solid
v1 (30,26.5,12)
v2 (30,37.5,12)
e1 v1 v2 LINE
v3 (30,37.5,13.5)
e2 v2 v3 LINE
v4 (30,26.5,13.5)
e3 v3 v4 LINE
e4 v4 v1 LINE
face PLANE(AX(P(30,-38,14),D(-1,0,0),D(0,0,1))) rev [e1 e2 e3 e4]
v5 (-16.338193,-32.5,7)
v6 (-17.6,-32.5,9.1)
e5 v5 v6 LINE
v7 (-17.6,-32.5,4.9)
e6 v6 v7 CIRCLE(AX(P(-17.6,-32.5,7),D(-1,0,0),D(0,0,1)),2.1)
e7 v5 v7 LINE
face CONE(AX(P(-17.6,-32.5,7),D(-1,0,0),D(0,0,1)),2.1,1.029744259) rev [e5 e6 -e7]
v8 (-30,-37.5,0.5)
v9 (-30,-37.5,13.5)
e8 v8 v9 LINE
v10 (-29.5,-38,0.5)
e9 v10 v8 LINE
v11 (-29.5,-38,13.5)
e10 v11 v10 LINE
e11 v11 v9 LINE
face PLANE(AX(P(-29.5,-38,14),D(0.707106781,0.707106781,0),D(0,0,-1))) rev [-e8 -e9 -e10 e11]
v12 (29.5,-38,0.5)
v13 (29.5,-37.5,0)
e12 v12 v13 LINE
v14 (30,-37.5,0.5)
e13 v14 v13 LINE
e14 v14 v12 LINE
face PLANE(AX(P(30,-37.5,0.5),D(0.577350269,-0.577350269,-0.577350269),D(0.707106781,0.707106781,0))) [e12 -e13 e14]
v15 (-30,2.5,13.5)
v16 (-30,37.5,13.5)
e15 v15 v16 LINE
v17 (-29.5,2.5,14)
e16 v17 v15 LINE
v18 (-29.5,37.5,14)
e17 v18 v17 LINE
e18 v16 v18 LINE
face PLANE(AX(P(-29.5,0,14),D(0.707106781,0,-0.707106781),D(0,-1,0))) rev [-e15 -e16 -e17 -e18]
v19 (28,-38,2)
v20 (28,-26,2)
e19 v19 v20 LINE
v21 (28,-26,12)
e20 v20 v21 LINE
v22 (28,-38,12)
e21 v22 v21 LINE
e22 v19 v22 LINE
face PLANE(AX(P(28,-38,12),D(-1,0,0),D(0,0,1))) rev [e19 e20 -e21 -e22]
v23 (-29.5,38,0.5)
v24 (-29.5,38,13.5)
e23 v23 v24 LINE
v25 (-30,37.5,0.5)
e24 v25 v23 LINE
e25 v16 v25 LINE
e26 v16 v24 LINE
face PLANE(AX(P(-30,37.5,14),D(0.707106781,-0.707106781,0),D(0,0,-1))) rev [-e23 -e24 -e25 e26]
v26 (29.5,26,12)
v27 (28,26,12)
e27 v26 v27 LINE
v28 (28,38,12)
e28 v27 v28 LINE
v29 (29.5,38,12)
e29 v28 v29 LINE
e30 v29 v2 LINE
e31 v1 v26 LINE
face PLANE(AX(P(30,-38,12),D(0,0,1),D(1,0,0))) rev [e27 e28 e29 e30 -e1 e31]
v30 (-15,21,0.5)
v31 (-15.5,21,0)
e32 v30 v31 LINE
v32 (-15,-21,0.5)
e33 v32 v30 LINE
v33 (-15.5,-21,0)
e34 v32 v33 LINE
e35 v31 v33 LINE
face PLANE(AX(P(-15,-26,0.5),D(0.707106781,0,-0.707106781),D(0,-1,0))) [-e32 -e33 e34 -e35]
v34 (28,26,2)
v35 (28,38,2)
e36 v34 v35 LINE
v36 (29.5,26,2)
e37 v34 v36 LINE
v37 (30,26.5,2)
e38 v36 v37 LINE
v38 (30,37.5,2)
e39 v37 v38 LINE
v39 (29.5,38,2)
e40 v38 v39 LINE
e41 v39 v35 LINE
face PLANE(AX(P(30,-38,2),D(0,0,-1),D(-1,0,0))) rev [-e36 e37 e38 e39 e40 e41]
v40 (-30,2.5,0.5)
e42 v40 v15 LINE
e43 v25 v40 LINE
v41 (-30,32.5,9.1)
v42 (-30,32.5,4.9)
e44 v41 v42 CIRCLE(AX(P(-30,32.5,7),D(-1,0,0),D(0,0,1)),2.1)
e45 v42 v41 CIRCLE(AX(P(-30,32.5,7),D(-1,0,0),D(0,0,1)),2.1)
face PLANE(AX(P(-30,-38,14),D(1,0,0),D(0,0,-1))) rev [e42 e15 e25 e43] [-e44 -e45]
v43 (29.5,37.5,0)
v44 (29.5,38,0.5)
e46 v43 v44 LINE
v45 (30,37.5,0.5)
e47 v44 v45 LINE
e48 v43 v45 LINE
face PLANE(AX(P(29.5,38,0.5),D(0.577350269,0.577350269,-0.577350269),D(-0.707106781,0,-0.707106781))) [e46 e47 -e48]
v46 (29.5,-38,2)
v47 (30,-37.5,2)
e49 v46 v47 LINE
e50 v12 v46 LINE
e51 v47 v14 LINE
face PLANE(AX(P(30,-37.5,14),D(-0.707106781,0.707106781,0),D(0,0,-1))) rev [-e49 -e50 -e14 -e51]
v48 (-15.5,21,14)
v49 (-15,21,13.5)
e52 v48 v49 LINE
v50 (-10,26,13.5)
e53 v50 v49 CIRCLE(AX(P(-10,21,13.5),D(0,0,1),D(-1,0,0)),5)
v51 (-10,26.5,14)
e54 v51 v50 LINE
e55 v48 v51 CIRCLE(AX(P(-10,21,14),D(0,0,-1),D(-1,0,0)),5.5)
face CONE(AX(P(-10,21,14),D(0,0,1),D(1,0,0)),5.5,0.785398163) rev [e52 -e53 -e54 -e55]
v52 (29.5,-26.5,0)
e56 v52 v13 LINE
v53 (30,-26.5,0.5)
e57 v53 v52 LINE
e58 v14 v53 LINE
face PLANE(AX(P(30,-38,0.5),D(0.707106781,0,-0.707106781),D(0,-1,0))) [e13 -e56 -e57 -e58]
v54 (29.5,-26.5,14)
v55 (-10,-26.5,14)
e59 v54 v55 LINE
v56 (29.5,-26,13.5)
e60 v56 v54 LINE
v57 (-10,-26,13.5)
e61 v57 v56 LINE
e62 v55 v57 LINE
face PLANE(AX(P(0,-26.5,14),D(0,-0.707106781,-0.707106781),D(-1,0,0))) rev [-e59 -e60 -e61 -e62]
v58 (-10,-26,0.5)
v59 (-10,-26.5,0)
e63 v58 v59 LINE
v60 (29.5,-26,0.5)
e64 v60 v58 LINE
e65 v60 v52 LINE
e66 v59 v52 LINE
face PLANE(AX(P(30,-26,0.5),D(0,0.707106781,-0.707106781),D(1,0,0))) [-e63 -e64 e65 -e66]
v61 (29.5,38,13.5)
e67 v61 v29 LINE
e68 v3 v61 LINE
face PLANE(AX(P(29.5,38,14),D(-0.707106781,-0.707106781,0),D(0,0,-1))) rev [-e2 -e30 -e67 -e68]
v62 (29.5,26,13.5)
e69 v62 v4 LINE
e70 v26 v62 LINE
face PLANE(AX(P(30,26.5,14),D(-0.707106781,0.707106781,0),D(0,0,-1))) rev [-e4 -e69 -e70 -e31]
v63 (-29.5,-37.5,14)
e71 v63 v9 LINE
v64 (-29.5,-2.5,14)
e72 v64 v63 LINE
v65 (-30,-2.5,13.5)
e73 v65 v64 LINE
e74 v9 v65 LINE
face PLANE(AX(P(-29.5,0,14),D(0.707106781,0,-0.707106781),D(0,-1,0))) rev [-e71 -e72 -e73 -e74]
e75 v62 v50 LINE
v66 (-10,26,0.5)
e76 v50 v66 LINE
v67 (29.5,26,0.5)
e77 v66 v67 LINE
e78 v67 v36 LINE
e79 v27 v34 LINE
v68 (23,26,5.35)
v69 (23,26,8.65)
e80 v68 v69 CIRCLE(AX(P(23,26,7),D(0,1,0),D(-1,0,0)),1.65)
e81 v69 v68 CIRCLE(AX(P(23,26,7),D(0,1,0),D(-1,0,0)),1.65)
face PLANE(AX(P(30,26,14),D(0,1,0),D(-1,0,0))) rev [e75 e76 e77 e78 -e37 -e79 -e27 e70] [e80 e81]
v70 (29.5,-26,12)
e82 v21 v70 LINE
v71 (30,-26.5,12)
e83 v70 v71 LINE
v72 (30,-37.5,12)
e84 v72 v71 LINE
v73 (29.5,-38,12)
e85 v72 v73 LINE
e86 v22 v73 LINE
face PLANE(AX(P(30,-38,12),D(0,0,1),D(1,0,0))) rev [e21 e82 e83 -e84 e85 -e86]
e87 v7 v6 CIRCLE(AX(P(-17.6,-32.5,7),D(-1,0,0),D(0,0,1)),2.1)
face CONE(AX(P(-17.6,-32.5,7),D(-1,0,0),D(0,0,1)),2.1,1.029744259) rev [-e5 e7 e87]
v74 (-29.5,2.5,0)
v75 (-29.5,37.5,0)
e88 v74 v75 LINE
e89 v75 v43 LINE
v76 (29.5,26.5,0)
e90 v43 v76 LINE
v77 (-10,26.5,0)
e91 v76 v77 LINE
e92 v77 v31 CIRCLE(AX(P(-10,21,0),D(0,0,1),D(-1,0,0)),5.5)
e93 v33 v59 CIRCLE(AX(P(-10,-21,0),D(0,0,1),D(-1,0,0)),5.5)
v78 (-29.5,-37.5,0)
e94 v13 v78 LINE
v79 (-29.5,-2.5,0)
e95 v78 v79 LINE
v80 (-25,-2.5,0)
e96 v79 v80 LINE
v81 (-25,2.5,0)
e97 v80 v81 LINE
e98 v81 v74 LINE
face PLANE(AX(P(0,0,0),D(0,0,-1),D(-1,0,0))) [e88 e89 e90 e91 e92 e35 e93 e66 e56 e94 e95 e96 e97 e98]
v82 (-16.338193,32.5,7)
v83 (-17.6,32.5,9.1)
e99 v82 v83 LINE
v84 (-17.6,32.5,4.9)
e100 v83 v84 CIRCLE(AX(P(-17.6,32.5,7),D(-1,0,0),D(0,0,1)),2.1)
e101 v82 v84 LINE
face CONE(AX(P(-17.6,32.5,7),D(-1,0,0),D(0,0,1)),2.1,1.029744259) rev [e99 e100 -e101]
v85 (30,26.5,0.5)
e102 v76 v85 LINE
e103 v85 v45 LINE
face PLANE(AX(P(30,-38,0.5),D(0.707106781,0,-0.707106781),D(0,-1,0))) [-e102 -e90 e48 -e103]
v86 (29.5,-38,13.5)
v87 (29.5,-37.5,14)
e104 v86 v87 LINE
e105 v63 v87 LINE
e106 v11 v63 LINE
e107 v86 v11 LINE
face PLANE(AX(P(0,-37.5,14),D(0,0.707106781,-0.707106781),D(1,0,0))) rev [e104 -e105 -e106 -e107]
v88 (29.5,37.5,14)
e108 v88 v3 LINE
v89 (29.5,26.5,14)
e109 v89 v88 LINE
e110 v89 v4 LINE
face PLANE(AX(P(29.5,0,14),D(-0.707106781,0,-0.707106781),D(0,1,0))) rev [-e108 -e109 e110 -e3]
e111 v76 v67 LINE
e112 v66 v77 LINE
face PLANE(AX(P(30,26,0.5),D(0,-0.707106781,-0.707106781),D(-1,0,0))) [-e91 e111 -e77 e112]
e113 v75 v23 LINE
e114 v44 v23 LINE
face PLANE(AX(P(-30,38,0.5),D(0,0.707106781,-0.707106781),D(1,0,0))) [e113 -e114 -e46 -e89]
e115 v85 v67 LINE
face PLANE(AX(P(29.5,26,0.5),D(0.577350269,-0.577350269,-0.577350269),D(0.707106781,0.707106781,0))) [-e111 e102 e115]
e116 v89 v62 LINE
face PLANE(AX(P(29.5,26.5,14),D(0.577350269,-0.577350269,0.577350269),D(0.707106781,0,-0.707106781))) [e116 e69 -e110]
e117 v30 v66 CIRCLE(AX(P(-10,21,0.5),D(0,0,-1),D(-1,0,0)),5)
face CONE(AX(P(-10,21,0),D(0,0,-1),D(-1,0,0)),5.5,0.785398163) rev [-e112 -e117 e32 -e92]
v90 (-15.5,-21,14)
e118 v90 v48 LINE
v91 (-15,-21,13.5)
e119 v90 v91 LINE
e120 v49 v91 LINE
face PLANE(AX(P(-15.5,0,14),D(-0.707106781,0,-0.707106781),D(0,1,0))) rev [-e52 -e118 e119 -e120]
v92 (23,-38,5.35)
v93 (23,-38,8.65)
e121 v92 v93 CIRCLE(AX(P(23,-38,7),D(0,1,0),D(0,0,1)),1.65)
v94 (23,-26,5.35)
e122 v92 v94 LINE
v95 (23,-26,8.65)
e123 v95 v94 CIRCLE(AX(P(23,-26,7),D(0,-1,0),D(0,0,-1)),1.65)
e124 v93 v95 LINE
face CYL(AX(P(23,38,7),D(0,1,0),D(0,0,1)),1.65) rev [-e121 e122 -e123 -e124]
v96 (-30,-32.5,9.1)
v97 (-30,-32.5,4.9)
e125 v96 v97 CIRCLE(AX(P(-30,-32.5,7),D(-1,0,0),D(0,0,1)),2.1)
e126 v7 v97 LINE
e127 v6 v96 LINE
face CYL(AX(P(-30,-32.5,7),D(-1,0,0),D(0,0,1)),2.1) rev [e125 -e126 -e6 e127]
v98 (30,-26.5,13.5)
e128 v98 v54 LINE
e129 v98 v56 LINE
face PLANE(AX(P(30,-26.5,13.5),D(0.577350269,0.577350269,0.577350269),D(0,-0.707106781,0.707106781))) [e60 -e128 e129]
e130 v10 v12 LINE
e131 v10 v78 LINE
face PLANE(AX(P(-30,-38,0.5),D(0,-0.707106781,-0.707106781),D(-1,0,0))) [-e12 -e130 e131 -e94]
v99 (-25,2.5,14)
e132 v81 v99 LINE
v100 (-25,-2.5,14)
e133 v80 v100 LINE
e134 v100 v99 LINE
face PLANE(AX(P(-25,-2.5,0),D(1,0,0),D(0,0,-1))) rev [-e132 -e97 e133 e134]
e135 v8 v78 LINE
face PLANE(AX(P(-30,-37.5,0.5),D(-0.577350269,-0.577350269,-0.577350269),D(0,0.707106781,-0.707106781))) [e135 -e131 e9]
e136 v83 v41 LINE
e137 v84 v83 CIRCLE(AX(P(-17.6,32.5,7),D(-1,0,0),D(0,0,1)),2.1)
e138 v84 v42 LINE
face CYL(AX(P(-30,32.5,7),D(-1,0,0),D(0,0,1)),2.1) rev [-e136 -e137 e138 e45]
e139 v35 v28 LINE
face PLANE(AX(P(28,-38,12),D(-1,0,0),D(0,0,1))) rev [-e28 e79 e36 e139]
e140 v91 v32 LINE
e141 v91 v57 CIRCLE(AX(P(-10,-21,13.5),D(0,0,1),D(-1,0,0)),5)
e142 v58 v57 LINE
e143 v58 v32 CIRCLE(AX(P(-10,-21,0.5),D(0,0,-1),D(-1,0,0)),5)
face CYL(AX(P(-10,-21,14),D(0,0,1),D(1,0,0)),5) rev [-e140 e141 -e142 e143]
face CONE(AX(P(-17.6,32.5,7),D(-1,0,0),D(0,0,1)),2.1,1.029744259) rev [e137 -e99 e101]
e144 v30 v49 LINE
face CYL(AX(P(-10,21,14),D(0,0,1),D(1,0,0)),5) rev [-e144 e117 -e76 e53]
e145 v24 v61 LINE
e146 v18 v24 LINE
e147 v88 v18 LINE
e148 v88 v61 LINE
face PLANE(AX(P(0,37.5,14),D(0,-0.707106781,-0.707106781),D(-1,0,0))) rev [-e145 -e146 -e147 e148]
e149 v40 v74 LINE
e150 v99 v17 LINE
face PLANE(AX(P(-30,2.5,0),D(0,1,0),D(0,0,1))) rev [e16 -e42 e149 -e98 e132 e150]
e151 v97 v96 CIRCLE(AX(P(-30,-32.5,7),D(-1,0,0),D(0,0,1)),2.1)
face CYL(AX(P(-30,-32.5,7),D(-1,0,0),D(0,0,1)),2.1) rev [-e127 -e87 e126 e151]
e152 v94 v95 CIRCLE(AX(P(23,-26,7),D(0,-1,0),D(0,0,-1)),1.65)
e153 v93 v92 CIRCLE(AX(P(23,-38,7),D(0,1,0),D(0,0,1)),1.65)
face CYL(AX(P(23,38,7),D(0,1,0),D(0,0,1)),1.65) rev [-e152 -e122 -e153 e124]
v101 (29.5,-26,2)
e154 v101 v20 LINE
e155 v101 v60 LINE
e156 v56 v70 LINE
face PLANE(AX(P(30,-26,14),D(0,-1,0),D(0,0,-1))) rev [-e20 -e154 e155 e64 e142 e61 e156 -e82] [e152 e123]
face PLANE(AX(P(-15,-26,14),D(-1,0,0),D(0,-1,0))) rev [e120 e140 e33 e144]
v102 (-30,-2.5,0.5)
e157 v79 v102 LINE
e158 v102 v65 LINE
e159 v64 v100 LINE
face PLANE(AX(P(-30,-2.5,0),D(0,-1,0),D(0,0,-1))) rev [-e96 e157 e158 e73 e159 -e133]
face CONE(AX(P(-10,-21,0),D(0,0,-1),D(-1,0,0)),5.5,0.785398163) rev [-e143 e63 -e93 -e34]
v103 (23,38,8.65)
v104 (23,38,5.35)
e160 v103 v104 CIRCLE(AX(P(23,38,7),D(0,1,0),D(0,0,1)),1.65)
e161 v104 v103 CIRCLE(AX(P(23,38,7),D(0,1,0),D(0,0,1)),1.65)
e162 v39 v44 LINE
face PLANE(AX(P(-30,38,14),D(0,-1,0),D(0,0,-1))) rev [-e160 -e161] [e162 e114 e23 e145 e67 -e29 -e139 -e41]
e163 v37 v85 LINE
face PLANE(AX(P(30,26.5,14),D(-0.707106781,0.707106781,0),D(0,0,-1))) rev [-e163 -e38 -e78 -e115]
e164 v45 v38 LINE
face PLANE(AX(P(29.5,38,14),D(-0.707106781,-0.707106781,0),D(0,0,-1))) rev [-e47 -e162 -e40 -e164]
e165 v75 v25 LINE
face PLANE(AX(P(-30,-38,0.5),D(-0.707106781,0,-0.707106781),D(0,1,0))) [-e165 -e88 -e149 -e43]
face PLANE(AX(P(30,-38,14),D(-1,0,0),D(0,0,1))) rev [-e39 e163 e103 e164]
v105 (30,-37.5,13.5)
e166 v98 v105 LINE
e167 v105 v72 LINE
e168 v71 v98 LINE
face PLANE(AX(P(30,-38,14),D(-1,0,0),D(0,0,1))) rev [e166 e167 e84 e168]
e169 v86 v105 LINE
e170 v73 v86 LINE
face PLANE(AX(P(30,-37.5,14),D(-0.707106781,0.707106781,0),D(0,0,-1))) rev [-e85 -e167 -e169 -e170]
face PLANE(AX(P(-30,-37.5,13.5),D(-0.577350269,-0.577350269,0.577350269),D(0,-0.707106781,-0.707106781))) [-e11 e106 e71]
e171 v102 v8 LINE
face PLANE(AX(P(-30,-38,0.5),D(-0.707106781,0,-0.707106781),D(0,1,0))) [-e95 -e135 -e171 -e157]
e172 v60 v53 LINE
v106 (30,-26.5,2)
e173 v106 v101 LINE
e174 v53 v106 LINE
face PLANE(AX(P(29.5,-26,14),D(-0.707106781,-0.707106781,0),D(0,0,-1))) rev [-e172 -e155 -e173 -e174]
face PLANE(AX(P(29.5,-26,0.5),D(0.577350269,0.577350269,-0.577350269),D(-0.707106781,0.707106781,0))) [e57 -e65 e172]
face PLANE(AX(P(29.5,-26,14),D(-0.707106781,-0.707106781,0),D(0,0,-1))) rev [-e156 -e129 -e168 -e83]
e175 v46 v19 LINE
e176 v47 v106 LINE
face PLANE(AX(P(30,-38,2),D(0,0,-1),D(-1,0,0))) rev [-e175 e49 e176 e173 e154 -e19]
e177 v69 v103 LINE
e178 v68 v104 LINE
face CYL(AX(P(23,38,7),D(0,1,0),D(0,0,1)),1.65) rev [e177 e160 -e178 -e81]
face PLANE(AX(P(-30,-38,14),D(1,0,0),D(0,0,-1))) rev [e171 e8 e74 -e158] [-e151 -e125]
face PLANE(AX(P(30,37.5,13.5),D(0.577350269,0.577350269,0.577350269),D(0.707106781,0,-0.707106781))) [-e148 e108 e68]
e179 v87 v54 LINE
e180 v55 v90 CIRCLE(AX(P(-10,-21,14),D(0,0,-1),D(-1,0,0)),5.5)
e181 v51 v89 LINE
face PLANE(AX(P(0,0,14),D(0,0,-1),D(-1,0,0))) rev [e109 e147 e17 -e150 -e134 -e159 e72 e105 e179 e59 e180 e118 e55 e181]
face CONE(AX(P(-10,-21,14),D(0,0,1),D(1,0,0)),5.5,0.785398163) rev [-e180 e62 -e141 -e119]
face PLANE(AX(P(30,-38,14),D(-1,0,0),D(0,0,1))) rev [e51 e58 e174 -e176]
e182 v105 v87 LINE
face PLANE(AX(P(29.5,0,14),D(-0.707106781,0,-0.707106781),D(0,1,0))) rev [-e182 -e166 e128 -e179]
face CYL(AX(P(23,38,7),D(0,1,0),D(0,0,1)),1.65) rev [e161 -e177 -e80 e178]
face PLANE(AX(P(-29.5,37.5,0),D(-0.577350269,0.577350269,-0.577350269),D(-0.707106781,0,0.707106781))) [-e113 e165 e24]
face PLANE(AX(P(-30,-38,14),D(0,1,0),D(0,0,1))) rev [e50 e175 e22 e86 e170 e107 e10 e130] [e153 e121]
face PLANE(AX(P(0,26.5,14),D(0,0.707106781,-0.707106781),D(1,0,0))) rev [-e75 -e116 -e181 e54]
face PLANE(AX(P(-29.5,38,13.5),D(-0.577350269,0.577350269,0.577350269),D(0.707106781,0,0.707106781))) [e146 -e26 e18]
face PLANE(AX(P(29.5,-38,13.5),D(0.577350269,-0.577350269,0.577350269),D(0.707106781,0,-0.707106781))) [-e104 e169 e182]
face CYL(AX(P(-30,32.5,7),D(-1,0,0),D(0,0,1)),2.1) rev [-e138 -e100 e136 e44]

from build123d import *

# Parameters (mm, degrees)
SKETCH_1_W             = 60
SKETCH_1_H             = 76
EXTRUDE_1_DEPTH        = 14
SKETCH_2_W             = 2
SKETCH_2_H             = 10
CUT_EXTRUDE_1_DEPTH    = 83.897527104
SKETCH_3_W             = 45
SKETCH_3_H             = 52
CUT_EXTRUDE_2_DEPTH    = 51.398412673
HOLE_WIZARD_M4_1_D     = 3.3
HOLE_WIZARD_M5_2_D     = 4.2
HOLE_WIZARD_M5_2_DEPTH = 12.4
HOLE_WIZARD_M5_2_TIP   = 1.2618073
SKETCH_8_W             = 5
SKETCH_8_H             = 5
CUT_EXTRUDE_3_DEPTH    = 51.398412673
FILLET_1_R             = 5
CHAMFER_1_SIZE         = 0.5


with BuildPart() as part:
    # 草图1 → 凸台-拉伸1 (new body)
    with BuildSketch(Plane.XY):
        Rectangle(SKETCH_1_W, SKETCH_1_H)
    extrude(amount=EXTRUDE_1_DEPTH)

    # 草图2 → 切除-拉伸1 (cut, through all)
    with BuildSketch(Plane(origin=(0, 38, 0), x_dir=(1, 0, 0), z_dir=(0, 1, 0))):
        with Locations((29, -7)):
            Rectangle(SKETCH_2_W, SKETCH_2_H)
    extrude(amount=-CUT_EXTRUDE_1_DEPTH, mode=Mode.SUBTRACT)

    # 草图3 → 切除-拉伸2 (cut, through all)
    with BuildSketch(Plane(origin=(0, 0, 0), x_dir=(-1, 0, 0), z_dir=(0, 0, -1))):
        with Locations((-7.5, 0)):
            Rectangle(SKETCH_3_W, SKETCH_3_H)
    extrude(amount=-CUT_EXTRUDE_2_DEPTH, mode=Mode.SUBTRACT)

    # M4 螺纹孔1 (through all)
    with Locations(Plane(origin=(0, 38, 0), x_dir=(1, 0, 0), z_dir=(0, 1, 0))):
        with Locations((23, -7)):
            Hole(HOLE_WIZARD_M4_1_D / 2)

    # M5 螺纹孔2
    with Locations(Plane.ZY.offset(30)):
        with Locations((7, 32.5), (7, -32.5)):
            Hole(HOLE_WIZARD_M5_2_D / 2, depth=HOLE_WIZARD_M5_2_DEPTH)
            with Locations((0, 0, -(HOLE_WIZARD_M5_2_DEPTH + HOLE_WIZARD_M5_2_TIP / 2))):  # 118° drill point
                Cone(0, HOLE_WIZARD_M5_2_D / 2, HOLE_WIZARD_M5_2_TIP, mode=Mode.SUBTRACT)

    # 草图8 → 切除-拉伸3 (cut, through all)
    with BuildSketch(Plane.XY.offset(14)):
        with Locations((-27.5, 0)):
            Rectangle(SKETCH_8_W, SKETCH_8_H)
    extrude(amount=-CUT_EXTRUDE_3_DEPTH, mode=Mode.SUBTRACT)

    # 圆角1
    fillet_1_edges = [part.edges().sort_by_distance(p)[0] for p in [
        (-15, -26, 7),
        (-15, 26, 7),
    ]]
    fillet(fillet_1_edges, radius=FILLET_1_R)

    # 倒角1
    chamfer_1_edges = [part.edges().sort_by_distance(p)[0] for p in [
        (-30, 20.25, 14),
        (30, -38, 1),
        (30, 38, 1),
        (0, -38, 14),
        (30, 32, 0),
        (30, 32, 14),
        (30, -26, 13),
        (30, -26, 1),
        (30, 26, 13),
        (30, 26, 1),
        (10, -26, 14),
        (10, -26, 0),
        (30, -32, 14),
        (0, -38, 0),
        (-30, 20.25, 0),
        (0, 38, 0),
        (30, -32, 0),
        (-30, -20.25, 0),
        (-30, -20.25, 14),
        (30, -38, 13),
        (-30, -38, 7),
        (-30, 38, 7),
        (30, 38, 13),
        (0, 38, 14),
        (10, 26, 14),
        (10, 26, 0),
        (-15, 0, 0),
        (-15, 0, 14),
        (-13.535533906, 24.535533906, 0),
        (-13.535533906, 24.535533906, 14),
        (-13.535533906, -24.535533906, 0),
        (-13.535533906, -24.535533906, 14),
    ]]
    chamfer(chamfer_1_edges, length=CHAMFER_1_SIZE)


solid = part.part
